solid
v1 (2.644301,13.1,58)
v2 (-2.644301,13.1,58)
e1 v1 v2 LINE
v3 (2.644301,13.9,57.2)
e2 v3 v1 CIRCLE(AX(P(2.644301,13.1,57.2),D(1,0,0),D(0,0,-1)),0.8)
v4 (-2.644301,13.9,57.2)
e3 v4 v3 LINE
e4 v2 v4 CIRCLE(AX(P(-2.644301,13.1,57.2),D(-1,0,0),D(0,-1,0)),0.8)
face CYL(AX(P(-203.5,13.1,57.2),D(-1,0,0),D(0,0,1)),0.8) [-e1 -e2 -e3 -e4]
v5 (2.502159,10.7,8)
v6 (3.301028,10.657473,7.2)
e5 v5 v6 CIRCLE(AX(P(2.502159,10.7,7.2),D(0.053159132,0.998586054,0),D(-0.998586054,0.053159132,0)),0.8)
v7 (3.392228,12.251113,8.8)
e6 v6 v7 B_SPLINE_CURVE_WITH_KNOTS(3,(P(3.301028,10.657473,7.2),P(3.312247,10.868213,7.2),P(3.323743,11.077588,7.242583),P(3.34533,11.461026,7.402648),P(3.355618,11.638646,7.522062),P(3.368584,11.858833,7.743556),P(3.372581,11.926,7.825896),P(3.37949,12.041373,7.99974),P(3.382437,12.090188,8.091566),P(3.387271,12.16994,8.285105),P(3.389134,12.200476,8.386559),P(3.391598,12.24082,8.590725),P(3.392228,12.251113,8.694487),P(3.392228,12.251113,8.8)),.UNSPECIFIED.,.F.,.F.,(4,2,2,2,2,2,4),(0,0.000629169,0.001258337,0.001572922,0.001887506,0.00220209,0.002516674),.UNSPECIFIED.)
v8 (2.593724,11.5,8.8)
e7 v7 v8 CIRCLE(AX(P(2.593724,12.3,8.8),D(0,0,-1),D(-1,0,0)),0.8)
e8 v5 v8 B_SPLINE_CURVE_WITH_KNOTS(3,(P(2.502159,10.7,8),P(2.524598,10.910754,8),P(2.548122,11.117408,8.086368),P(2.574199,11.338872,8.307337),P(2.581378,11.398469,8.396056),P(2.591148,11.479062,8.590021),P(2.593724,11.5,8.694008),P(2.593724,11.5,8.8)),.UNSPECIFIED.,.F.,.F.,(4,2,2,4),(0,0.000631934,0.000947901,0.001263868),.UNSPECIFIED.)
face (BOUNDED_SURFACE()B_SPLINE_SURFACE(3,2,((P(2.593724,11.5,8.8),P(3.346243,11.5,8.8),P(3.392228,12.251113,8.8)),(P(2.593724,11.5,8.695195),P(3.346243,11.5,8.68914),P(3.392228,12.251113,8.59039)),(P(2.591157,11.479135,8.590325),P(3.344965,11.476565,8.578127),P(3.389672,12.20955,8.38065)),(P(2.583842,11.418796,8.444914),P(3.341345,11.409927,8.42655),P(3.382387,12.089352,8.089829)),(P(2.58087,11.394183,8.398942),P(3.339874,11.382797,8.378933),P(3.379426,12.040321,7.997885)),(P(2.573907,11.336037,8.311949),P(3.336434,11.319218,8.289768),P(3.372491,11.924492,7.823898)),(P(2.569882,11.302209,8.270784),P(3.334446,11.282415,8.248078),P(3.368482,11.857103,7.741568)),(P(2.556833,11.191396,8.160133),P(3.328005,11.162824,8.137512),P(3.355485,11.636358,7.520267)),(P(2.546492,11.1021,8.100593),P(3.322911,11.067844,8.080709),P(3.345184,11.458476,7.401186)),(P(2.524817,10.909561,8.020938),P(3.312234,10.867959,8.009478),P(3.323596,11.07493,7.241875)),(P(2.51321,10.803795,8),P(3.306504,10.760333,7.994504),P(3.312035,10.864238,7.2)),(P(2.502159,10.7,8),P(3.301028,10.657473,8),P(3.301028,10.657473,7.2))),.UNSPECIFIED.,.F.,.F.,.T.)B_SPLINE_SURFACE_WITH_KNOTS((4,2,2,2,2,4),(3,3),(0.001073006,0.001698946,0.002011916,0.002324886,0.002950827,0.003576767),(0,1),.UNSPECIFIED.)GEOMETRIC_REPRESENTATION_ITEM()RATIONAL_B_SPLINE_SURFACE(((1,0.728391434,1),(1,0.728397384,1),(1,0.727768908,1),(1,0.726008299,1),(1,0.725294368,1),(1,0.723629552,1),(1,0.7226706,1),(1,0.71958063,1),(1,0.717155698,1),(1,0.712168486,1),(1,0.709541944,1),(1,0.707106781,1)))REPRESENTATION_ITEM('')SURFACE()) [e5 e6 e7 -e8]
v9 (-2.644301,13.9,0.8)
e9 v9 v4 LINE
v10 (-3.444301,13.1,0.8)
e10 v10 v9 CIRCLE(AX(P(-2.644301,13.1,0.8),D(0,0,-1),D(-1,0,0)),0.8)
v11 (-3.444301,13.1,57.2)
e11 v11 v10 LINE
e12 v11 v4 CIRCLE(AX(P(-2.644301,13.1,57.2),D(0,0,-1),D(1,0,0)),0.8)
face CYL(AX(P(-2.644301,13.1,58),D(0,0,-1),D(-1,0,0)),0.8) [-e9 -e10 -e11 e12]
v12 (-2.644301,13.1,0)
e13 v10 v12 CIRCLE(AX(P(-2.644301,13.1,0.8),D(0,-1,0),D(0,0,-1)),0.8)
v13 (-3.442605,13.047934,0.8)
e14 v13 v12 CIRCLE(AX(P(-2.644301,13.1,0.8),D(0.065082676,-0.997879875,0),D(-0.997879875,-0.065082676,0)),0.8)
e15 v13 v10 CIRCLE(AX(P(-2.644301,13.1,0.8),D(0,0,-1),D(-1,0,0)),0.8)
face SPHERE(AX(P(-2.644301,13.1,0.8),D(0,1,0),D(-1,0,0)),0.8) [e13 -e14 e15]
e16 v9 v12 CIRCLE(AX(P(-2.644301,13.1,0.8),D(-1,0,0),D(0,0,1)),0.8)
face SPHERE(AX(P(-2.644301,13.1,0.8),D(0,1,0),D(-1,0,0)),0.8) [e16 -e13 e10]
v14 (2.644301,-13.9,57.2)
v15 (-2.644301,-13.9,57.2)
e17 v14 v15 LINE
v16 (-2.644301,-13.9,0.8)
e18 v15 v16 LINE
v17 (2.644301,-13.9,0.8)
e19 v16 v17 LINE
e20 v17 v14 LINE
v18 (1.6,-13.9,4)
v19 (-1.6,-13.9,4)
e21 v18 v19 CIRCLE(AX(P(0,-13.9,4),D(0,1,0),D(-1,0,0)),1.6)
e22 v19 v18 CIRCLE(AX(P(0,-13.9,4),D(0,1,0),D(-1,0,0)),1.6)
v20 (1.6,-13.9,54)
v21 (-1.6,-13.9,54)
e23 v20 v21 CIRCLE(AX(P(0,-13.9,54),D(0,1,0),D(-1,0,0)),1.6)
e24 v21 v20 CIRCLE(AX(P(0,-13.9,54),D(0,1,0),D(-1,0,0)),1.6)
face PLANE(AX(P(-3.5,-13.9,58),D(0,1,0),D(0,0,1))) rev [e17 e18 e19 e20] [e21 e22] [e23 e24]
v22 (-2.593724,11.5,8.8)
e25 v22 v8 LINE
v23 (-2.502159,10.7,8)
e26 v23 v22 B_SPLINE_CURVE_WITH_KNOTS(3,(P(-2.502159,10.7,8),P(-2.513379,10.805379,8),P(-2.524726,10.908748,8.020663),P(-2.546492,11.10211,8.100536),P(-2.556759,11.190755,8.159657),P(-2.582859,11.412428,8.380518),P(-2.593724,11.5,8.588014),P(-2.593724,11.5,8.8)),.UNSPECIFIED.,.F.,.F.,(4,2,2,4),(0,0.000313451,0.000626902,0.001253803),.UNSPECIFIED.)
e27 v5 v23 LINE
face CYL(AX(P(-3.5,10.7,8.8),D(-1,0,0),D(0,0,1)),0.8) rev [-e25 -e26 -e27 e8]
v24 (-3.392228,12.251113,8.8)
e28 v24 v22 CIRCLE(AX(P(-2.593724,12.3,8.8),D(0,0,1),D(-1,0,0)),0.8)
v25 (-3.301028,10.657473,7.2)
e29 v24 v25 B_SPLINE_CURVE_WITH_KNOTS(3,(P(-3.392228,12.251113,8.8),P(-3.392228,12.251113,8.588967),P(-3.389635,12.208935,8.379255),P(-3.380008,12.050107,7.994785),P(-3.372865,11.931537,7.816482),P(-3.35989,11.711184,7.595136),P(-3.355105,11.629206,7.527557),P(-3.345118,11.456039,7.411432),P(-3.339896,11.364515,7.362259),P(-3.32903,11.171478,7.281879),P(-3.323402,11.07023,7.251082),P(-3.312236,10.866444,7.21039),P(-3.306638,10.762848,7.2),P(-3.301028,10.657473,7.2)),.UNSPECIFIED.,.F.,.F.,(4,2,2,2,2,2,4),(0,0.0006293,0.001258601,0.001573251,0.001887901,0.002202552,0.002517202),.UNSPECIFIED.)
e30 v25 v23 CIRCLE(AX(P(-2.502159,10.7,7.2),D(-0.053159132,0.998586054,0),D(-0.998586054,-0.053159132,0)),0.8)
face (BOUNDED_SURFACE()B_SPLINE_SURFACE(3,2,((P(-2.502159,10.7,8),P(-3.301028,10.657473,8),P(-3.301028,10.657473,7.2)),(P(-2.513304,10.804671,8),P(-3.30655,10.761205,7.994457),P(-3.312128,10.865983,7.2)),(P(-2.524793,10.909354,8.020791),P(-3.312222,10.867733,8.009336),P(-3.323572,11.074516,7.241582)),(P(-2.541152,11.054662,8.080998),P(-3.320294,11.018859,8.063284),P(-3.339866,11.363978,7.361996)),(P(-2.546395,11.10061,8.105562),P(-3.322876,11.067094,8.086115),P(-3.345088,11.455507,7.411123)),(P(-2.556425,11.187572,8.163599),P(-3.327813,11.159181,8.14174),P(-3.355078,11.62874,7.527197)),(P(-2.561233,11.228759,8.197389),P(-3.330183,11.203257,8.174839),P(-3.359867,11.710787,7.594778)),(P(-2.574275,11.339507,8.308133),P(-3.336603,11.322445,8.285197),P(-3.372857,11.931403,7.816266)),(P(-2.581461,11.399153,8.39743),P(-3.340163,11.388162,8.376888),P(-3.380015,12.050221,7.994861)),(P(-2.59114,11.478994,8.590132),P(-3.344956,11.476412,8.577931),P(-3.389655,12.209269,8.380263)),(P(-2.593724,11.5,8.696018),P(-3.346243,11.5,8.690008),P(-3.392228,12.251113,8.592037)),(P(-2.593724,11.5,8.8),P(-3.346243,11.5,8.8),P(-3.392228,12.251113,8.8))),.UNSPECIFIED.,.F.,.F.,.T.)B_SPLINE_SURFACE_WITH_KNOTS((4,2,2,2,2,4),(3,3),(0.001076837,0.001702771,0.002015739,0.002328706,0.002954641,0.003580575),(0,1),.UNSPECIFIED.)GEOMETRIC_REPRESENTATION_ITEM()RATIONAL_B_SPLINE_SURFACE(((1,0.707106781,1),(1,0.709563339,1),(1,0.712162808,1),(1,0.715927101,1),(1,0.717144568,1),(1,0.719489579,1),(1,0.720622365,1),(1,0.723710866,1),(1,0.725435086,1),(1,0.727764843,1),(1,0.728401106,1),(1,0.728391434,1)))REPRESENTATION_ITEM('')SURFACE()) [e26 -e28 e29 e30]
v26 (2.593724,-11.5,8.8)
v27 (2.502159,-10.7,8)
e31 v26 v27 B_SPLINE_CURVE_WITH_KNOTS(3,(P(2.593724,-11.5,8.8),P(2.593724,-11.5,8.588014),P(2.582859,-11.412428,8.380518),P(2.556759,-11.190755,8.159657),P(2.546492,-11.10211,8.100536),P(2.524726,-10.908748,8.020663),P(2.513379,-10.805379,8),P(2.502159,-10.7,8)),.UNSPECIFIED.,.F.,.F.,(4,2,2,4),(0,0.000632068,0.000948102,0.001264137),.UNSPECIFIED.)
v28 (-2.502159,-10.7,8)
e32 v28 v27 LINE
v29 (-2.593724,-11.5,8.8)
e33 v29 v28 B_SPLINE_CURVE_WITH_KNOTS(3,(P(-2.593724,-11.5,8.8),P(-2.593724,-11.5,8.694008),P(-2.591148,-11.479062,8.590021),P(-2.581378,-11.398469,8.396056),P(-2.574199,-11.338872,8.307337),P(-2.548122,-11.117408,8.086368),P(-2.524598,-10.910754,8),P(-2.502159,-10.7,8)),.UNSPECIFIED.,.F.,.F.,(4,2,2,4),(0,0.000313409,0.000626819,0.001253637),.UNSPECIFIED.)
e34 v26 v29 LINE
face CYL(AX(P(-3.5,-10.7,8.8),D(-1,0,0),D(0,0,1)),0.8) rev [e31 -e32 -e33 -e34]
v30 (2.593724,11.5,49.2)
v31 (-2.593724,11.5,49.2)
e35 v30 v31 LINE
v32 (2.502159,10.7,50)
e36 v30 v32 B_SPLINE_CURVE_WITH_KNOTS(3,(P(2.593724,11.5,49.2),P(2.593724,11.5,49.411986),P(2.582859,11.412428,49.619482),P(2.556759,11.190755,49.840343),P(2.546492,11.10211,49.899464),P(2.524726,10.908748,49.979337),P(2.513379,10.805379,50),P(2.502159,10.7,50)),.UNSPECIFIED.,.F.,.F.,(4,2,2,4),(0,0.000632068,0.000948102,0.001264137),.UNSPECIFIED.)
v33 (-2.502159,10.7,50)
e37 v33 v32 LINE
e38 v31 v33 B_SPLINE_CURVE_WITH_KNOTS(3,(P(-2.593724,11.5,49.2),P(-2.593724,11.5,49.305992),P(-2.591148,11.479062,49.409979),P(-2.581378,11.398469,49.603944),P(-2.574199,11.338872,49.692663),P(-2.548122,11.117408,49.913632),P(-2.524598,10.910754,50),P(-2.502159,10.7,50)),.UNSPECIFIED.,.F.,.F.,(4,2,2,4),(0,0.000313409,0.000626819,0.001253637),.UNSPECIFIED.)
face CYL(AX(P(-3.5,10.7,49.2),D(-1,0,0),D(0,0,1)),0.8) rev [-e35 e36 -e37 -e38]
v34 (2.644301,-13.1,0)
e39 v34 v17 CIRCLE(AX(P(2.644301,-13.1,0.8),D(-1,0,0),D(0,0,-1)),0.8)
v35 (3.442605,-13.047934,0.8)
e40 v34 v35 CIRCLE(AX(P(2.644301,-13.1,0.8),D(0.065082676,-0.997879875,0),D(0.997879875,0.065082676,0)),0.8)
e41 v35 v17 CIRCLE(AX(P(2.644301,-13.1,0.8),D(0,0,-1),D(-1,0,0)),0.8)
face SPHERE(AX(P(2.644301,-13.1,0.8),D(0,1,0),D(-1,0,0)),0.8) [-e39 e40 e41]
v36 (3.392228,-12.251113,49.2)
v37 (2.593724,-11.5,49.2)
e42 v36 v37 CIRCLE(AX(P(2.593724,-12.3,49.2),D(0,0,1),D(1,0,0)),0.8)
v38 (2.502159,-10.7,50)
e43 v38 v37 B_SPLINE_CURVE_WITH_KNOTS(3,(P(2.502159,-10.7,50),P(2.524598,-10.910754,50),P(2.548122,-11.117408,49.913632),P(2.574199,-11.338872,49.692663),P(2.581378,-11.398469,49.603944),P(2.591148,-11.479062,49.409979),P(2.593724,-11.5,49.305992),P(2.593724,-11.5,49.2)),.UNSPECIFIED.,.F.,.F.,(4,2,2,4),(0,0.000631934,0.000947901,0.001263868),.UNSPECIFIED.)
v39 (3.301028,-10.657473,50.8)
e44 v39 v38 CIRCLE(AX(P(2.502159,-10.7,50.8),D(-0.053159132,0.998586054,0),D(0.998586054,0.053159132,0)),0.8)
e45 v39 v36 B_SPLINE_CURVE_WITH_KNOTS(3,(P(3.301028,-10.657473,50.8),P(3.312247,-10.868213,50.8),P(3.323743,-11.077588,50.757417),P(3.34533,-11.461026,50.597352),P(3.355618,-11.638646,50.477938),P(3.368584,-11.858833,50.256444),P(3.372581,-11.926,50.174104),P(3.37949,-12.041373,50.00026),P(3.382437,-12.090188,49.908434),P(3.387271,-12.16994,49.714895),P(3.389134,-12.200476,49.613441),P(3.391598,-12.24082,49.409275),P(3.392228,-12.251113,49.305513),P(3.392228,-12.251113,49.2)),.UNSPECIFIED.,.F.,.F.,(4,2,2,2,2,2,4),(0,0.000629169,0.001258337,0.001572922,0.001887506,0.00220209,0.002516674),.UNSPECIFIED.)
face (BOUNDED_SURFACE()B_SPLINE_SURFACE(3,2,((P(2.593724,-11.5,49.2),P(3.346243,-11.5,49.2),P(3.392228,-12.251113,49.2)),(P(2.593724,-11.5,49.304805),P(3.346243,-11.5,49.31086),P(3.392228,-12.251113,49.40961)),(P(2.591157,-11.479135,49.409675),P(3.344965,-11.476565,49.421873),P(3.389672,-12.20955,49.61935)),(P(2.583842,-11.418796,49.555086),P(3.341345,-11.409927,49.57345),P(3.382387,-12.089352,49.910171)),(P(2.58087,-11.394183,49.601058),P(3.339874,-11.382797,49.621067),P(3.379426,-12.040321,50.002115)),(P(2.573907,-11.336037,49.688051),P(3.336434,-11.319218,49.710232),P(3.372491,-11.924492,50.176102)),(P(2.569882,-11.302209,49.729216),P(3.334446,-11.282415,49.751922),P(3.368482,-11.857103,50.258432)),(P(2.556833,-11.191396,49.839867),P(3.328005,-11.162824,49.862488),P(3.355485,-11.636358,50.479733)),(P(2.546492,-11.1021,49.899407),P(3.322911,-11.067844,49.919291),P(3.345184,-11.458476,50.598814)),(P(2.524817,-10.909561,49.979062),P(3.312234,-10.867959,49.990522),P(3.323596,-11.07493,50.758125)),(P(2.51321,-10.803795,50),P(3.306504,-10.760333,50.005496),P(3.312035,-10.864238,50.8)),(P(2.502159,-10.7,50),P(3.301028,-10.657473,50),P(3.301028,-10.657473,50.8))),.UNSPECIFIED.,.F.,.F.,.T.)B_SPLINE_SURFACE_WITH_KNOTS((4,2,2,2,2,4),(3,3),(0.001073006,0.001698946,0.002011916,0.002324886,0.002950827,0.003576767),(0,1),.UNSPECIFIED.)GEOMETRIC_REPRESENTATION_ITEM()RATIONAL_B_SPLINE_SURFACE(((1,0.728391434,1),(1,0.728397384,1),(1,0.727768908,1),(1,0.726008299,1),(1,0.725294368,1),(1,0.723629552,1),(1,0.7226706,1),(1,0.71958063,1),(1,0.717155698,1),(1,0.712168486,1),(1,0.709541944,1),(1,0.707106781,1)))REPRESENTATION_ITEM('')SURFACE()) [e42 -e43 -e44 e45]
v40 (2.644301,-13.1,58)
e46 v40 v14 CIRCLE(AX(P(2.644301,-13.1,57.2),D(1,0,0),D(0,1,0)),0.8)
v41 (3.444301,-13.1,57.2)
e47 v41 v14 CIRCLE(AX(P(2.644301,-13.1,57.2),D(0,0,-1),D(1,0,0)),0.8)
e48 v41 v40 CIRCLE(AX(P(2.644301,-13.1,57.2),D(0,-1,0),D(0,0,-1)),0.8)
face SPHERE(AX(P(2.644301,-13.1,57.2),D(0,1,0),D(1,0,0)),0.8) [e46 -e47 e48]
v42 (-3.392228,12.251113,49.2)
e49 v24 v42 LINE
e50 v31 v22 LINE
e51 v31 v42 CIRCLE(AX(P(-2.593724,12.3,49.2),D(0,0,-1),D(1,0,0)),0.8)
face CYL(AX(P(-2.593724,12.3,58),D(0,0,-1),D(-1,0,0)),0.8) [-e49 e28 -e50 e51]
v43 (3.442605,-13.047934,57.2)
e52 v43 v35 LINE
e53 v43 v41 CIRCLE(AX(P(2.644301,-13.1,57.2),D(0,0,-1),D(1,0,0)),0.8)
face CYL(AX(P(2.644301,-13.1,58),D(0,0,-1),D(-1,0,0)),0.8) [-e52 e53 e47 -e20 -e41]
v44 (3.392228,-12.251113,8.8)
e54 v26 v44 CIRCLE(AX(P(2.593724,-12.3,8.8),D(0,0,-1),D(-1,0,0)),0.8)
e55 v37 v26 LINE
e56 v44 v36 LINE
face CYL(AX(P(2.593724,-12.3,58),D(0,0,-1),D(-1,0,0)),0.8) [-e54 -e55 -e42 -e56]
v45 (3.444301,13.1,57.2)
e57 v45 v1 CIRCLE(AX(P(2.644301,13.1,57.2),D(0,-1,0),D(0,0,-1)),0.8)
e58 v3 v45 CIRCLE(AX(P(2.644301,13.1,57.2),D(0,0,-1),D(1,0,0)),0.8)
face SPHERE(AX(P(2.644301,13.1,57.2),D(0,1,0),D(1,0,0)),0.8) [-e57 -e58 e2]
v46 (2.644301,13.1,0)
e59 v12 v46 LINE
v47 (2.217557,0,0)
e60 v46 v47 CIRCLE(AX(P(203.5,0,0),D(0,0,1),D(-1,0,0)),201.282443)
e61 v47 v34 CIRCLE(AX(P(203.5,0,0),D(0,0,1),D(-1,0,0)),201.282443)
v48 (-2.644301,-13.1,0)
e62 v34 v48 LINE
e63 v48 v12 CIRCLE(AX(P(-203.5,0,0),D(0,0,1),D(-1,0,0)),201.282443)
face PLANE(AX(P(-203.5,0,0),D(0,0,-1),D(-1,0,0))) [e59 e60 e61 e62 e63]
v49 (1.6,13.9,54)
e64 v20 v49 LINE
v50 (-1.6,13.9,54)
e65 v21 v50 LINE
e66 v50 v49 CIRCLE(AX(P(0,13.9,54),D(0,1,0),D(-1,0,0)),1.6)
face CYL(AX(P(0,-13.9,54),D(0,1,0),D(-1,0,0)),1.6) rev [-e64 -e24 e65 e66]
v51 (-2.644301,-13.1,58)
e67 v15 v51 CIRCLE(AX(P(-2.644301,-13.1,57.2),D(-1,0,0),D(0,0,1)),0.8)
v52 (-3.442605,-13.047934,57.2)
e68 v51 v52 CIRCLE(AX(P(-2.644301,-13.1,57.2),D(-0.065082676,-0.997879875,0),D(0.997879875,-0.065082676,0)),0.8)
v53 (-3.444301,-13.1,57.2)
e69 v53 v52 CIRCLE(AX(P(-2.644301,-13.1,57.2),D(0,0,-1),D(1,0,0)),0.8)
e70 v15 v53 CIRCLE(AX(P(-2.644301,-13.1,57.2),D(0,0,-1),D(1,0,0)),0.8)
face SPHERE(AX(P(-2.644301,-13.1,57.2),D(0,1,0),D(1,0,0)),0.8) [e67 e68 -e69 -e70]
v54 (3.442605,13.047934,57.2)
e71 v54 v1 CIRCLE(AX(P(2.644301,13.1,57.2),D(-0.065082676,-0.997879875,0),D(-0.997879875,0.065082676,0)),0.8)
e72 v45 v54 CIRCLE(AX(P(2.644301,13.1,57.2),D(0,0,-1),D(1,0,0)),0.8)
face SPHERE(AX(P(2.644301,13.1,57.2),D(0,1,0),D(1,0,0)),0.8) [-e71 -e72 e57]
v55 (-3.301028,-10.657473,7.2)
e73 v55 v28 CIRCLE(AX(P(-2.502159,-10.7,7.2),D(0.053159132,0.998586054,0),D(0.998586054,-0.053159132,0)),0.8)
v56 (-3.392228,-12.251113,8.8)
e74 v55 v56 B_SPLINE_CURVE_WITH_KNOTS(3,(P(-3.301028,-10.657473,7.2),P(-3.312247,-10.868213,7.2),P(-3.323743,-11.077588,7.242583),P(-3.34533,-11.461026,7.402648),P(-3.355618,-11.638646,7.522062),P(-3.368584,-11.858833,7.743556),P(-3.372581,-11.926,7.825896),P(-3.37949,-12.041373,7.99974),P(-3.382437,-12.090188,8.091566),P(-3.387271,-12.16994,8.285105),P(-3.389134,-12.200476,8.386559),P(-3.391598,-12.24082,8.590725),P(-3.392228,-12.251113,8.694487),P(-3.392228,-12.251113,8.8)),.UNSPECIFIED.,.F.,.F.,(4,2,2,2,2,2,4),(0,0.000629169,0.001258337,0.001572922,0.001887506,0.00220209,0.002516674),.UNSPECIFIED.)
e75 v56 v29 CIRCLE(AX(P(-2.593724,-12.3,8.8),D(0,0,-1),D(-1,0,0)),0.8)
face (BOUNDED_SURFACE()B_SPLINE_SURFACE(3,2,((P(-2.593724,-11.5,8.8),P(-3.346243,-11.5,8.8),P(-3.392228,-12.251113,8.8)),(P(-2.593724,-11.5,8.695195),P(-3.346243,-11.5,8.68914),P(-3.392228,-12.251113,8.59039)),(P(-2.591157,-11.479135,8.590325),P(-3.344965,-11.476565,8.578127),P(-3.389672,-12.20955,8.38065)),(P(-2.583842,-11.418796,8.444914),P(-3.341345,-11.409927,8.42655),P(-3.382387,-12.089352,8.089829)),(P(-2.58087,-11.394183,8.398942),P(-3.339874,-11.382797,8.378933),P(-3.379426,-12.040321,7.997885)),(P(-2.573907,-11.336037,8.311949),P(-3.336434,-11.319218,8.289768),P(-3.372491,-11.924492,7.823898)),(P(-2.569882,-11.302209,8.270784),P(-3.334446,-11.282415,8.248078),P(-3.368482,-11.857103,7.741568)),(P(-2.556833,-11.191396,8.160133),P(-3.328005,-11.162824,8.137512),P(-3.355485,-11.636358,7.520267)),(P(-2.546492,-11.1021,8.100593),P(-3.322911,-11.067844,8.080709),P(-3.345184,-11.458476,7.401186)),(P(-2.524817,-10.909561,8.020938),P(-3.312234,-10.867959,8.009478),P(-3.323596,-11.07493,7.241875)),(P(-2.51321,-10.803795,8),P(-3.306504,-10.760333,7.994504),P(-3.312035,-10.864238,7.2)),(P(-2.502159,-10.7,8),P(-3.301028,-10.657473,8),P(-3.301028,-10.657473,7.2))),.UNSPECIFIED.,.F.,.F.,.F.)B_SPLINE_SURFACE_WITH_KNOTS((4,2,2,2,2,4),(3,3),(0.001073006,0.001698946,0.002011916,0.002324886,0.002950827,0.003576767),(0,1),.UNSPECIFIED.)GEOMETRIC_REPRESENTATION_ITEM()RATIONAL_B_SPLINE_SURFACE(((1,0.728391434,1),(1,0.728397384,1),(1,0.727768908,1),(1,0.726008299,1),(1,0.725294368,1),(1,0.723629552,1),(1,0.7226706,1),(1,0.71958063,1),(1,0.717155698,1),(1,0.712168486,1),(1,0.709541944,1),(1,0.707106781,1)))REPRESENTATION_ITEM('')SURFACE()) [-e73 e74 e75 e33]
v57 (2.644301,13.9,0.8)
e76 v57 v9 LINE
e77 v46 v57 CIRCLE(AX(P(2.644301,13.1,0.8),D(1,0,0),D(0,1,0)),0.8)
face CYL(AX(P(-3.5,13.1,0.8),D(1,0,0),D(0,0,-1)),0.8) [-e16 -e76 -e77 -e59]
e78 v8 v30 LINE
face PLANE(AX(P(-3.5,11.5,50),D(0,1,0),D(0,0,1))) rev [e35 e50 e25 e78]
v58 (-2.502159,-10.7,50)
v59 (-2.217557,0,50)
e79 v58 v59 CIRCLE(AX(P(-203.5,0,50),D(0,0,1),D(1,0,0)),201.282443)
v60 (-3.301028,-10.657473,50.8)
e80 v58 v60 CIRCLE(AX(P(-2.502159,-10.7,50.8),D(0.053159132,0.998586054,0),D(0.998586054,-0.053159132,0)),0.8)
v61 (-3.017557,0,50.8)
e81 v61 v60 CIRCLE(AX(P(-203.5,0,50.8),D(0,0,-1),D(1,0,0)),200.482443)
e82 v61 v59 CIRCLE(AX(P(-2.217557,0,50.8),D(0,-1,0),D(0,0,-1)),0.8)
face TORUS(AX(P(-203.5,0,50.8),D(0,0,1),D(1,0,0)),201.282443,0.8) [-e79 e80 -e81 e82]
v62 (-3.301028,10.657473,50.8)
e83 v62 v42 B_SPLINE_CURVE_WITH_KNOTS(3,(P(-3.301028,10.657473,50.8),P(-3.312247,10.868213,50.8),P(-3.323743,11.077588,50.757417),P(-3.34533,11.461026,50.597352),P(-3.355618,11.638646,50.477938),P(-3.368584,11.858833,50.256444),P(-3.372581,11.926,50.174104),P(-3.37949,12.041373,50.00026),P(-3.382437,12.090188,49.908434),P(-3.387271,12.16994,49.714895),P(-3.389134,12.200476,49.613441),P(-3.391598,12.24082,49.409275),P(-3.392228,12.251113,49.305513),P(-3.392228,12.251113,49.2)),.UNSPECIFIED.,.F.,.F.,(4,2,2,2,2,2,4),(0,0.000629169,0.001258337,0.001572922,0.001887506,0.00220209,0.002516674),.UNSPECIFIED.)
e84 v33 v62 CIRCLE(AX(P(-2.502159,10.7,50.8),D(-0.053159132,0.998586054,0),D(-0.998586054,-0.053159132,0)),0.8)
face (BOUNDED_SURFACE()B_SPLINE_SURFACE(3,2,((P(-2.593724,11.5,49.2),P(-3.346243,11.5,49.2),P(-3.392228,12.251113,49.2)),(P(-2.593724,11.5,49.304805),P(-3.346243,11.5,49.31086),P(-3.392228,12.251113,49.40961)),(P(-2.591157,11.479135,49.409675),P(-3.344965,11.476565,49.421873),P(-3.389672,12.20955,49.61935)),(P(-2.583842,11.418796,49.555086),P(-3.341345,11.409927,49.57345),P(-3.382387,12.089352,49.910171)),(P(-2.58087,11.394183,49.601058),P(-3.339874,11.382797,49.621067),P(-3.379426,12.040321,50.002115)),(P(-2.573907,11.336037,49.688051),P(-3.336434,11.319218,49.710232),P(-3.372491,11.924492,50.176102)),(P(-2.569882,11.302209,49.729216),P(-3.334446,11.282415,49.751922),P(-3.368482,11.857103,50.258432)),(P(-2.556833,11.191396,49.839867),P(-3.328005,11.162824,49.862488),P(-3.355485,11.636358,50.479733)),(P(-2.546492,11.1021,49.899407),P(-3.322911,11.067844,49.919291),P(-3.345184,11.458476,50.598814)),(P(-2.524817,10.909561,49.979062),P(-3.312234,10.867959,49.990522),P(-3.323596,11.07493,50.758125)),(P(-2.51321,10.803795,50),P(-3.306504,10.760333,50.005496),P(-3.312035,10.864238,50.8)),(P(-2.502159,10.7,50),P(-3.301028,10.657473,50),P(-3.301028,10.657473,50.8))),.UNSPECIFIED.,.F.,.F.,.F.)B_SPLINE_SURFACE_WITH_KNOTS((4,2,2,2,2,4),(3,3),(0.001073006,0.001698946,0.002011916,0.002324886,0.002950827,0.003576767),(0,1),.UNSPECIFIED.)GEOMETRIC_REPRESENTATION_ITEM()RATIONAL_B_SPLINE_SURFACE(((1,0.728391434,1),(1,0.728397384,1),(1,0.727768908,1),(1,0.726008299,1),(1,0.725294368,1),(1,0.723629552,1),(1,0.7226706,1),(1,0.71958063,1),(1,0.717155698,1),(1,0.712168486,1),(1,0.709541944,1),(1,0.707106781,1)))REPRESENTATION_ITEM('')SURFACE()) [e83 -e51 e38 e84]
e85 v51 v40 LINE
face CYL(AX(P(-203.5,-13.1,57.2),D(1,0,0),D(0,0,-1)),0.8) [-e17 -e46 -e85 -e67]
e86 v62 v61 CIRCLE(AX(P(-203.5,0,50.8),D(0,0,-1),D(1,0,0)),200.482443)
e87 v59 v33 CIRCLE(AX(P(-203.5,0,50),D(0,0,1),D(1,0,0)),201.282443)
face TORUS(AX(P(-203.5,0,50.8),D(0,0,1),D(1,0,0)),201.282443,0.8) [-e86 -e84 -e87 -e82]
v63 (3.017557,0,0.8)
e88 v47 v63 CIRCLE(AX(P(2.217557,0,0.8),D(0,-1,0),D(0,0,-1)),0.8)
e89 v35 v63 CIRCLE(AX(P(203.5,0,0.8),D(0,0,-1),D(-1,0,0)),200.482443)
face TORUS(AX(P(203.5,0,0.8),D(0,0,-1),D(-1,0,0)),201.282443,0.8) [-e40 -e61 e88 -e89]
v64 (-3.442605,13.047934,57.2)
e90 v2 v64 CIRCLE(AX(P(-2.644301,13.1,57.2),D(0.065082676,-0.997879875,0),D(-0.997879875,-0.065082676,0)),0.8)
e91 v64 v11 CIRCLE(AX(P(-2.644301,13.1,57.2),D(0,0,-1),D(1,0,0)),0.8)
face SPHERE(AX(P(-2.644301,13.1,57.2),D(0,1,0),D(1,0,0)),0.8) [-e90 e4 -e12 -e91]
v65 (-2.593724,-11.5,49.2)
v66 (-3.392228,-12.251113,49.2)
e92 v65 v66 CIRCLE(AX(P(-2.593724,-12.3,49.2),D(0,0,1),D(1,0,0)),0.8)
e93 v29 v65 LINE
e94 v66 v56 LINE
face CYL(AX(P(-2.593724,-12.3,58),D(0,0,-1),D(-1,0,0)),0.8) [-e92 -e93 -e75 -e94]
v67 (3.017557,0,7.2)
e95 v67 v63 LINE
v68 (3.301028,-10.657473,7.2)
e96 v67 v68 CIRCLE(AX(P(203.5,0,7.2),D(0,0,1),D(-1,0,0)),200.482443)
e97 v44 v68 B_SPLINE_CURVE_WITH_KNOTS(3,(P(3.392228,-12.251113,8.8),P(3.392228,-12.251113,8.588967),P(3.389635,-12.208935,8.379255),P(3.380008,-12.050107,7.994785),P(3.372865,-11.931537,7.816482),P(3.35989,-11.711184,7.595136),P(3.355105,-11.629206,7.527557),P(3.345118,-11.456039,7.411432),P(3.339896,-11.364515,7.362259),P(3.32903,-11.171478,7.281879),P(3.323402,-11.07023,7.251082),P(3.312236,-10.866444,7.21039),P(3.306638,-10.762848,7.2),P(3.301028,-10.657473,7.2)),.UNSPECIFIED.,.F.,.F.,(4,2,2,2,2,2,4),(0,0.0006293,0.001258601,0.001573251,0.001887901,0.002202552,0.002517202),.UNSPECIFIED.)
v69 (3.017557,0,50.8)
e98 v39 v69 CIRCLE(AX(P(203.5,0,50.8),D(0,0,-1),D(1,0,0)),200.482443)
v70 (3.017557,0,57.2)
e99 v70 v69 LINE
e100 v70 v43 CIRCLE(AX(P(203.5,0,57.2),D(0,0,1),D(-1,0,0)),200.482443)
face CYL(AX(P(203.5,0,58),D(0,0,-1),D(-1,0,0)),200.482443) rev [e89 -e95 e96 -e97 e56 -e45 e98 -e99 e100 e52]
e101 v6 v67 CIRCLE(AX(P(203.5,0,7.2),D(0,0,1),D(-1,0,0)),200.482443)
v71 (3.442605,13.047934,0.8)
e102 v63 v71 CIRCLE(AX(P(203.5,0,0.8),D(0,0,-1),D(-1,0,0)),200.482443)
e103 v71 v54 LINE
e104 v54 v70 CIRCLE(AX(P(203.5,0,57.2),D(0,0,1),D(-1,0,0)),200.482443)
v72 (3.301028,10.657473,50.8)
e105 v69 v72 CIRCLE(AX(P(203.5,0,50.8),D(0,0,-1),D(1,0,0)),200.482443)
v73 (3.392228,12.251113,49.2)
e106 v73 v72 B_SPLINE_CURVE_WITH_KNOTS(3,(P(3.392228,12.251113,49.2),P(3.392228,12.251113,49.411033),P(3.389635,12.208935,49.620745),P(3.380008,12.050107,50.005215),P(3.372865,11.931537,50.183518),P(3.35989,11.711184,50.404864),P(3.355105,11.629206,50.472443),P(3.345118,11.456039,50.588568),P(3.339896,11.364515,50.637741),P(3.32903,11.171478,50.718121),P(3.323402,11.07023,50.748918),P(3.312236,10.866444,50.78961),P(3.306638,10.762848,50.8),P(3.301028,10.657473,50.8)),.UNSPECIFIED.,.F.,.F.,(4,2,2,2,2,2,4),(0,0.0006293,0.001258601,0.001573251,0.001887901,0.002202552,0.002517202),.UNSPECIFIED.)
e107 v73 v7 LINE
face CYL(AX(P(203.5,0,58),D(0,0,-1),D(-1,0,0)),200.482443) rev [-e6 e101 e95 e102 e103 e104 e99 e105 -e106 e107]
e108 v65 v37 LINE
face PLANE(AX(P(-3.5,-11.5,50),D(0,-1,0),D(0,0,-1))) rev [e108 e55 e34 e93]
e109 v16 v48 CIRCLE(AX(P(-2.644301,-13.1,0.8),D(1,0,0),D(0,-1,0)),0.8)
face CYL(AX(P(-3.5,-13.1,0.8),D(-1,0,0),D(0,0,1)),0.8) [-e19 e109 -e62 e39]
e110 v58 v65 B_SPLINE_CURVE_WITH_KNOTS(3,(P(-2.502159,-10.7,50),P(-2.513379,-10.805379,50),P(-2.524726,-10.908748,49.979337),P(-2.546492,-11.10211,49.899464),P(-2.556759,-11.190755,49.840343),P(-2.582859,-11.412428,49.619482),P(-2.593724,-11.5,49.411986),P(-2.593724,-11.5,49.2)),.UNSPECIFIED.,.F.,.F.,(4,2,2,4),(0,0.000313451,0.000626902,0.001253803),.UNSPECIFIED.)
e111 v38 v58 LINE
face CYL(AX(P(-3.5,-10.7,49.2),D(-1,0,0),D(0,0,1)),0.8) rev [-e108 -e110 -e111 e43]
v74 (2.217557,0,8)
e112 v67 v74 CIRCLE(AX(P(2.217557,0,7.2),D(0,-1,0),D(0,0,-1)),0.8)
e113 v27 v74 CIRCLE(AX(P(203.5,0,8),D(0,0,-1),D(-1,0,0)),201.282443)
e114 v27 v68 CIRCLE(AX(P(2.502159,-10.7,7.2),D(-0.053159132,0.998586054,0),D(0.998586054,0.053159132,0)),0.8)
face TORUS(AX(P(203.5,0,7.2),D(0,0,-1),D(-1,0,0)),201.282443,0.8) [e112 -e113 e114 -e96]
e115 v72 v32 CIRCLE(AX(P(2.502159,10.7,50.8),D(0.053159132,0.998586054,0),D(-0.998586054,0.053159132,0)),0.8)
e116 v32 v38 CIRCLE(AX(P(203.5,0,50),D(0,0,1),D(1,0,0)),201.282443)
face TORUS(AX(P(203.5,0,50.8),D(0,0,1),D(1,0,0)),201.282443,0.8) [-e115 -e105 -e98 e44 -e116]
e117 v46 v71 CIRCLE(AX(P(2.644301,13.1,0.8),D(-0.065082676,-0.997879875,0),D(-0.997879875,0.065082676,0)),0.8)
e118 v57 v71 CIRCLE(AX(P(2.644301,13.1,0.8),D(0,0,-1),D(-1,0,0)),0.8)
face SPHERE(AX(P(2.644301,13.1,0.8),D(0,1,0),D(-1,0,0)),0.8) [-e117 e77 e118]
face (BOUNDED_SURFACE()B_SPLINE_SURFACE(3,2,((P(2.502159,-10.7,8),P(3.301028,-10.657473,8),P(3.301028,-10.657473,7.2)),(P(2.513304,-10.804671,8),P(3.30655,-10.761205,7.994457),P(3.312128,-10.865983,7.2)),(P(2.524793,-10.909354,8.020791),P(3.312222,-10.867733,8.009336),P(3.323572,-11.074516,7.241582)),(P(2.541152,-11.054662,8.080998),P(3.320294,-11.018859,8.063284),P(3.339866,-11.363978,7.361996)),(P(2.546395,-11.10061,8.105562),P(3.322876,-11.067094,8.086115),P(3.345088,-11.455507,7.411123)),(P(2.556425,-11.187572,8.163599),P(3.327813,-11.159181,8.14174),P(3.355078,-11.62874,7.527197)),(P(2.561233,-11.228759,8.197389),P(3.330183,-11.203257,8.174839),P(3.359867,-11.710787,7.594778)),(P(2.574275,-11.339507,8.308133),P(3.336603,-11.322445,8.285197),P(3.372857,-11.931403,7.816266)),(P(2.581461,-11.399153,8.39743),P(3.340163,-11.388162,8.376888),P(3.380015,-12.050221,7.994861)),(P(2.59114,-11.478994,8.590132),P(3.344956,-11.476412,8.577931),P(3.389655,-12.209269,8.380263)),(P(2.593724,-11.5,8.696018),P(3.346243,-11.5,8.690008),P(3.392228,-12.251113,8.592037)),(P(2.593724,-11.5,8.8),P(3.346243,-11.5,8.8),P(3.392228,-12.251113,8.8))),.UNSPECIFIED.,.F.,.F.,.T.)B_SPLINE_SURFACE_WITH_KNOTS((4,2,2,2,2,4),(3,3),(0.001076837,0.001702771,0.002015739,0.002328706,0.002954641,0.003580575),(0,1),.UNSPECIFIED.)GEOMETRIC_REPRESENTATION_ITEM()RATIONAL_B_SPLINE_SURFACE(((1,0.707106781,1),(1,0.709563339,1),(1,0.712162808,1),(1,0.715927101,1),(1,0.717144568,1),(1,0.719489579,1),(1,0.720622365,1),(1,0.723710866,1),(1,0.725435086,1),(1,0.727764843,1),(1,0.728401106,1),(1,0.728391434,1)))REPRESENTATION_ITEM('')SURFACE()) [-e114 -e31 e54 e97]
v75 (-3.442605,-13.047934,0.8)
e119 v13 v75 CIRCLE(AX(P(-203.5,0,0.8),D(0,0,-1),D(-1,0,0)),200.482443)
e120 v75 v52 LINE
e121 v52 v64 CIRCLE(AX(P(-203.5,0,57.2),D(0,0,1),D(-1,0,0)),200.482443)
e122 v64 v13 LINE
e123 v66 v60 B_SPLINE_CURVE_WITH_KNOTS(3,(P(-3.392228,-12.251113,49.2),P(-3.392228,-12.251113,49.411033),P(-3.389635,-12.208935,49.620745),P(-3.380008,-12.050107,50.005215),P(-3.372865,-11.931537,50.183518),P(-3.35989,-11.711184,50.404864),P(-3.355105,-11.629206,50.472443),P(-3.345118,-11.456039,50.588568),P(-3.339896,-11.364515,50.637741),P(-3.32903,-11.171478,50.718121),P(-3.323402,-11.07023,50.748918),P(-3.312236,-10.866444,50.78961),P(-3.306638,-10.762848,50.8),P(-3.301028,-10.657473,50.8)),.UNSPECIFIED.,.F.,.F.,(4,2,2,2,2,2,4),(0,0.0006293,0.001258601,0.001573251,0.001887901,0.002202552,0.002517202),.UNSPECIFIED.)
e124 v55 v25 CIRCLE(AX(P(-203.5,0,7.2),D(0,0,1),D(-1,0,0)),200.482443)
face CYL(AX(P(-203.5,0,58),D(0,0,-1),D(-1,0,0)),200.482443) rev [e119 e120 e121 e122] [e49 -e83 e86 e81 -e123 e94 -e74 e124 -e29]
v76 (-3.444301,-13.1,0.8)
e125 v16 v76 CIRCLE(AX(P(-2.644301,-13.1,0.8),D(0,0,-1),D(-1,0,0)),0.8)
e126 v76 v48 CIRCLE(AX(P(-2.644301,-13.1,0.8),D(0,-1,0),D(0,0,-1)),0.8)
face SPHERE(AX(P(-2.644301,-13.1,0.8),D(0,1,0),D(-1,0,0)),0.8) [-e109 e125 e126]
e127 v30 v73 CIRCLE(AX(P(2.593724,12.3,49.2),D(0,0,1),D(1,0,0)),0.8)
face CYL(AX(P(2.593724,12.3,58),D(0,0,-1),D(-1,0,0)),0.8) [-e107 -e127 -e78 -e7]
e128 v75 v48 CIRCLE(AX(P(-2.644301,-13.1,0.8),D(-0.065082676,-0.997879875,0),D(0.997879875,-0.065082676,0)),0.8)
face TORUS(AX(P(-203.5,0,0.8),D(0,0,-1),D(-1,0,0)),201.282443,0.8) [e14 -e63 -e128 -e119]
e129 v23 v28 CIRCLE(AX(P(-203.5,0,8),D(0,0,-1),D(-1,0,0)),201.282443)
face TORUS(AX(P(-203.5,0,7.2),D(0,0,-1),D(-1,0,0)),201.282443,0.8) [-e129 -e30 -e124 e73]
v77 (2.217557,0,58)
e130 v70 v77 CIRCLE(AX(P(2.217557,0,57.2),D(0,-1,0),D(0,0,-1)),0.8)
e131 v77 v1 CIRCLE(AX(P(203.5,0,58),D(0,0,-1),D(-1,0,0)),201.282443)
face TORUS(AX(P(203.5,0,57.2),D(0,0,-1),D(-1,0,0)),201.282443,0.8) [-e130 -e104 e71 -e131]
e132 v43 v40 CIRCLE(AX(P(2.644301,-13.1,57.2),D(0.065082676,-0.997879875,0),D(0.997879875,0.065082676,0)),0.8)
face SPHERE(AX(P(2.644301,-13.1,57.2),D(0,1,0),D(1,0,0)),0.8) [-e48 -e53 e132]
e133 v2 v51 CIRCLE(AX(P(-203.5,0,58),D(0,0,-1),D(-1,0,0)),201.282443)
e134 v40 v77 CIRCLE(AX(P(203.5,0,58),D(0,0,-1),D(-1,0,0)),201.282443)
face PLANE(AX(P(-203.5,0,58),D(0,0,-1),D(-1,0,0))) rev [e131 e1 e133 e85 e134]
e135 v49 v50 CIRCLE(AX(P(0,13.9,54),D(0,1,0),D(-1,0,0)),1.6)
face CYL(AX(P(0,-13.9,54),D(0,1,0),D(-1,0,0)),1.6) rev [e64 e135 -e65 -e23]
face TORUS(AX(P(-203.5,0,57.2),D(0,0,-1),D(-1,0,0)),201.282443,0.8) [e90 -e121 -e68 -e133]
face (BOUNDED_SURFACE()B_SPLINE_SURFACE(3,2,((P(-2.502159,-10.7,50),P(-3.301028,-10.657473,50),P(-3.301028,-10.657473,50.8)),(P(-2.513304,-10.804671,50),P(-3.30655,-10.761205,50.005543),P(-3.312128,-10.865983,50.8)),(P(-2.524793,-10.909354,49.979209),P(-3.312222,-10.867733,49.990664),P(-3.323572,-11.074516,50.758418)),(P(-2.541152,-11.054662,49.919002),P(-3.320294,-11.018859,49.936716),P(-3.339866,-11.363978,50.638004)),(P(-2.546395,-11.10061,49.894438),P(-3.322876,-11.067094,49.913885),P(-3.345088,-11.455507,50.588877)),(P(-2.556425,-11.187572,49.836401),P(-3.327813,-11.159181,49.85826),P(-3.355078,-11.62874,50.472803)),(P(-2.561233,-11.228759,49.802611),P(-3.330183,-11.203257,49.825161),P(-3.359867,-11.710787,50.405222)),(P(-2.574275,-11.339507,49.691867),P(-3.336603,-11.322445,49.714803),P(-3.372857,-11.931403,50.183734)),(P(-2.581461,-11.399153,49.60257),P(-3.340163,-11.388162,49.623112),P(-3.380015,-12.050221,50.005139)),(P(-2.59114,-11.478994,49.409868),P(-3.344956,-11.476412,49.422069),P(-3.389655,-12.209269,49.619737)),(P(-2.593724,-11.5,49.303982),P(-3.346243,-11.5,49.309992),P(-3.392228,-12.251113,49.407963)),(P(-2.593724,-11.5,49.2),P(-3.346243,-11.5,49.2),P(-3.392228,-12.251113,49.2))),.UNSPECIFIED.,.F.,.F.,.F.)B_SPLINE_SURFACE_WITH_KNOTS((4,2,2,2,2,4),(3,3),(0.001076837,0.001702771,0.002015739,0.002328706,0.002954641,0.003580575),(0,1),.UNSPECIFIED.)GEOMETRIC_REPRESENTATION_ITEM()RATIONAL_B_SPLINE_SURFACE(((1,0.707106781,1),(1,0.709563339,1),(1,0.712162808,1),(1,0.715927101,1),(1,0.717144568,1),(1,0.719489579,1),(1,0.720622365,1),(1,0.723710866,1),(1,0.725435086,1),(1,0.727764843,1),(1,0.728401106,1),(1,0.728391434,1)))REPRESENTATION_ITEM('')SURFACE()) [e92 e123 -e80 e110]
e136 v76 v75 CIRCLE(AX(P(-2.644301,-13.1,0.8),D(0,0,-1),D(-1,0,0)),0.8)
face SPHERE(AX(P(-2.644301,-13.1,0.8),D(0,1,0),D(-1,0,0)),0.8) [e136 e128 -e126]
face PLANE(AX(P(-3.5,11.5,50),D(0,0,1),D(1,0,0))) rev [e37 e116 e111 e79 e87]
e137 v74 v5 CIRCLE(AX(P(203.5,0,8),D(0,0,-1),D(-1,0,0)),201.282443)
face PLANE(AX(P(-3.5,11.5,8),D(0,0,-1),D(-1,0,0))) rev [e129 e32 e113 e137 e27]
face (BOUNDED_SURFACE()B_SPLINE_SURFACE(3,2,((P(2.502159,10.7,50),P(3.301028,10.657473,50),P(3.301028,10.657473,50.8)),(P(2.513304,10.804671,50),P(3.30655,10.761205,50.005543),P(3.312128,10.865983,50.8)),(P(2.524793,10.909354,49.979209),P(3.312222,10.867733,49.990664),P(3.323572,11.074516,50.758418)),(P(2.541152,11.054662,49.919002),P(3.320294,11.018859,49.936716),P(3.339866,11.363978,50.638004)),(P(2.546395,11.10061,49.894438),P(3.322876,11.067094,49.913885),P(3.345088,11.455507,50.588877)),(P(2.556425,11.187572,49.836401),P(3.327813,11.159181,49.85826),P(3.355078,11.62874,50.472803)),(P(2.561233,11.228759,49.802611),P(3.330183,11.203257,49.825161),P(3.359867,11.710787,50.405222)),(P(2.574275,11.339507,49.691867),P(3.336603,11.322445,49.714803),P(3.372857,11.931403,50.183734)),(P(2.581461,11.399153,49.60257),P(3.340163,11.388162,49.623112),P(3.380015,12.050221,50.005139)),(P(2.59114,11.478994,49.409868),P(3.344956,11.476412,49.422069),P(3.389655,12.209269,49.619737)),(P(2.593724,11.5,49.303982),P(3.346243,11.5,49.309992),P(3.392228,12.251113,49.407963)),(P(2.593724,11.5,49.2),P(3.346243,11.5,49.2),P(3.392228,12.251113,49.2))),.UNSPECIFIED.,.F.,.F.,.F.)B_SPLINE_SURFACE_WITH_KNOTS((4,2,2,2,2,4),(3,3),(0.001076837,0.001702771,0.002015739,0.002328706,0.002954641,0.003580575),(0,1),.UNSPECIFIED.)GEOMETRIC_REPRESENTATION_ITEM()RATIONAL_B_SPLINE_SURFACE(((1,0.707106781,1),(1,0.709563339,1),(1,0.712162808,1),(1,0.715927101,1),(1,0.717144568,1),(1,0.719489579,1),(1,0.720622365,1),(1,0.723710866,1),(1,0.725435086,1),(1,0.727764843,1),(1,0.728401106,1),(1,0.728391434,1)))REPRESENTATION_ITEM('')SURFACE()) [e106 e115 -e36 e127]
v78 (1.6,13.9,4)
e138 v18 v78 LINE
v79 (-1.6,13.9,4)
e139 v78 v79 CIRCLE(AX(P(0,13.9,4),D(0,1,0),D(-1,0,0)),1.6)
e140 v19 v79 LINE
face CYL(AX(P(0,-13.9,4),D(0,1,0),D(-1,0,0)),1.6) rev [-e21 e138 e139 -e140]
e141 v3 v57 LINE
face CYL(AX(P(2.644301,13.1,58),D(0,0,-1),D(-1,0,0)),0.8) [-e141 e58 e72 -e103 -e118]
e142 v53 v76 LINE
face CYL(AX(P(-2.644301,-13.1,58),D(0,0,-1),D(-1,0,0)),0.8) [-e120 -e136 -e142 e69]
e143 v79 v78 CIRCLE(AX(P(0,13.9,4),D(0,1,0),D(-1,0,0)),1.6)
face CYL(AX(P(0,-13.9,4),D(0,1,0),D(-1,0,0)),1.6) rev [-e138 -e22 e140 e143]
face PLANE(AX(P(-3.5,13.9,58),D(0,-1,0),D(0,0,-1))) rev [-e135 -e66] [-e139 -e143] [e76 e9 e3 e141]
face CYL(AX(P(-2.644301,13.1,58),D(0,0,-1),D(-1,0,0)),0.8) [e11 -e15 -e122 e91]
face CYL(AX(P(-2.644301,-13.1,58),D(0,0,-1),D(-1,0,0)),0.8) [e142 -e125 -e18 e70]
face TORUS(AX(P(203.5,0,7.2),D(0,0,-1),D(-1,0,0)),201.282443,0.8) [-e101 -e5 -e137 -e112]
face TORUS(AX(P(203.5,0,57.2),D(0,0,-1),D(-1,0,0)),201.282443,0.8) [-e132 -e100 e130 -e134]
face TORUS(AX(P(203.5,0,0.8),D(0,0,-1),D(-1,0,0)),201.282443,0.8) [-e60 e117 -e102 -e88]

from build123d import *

# Parameters (mm, degrees)
EXTRUDE_1_DEPTH          = 58
CUT_EXTRUDE_1_DEPTH      = 60.744957946
CUT_EXTRUDE_1_DEPTH_BACK = 60.744957946
SKETCH_2_W               = 42
SKETCH_2_H               = 23
SKETCH_3_R               = 1.6
CUT_EXTRUDE_2_DEPTH      = 65.413430277
FILLET_1_R               = 0.8


with BuildPart() as part:
    # 草图1 → 凸台-拉伸1 (new body)
    with BuildSketch(Plane.XY):
        with BuildLine():
            Line((-3.5, 13.9), (3.5, 13.9))
            ThreePointArc((3.5, 13.9), (3.017556878, 0), (3.5, -13.9))
            Line((3.5, -13.9), (-3.5, -13.9))
            ThreePointArc((-3.5, -13.9), (-3.017556878, 0), (-3.5, 13.9))
        make_face()
    extrude(amount=EXTRUDE_1_DEPTH)

    # 草图2 → 切除-拉伸1 (cut, two sides: drawn at the far end of the back side and taken through both)
    with BuildSketch(Plane(origin=(0, 0, 0), x_dir=(0, 0, -1), z_dir=(1, 0, 0)).offset(-CUT_EXTRUDE_1_DEPTH_BACK)):
        with Locations((-29, 0)):
            Rectangle(SKETCH_2_W, SKETCH_2_H)
    extrude(amount=CUT_EXTRUDE_1_DEPTH + CUT_EXTRUDE_1_DEPTH_BACK, mode=Mode.SUBTRACT)

    # 草图3 → 切除-拉伸2 (cut, through all)
    with BuildSketch(Plane(origin=(0, 13.9, 0), x_dir=(1, 0, 0), z_dir=(0, 1, 0))):
        with Locations(Location((0, -4, 0), (0, 0, 180))):
            Circle(SKETCH_3_R)
        with Locations(Location((0, -54, 0), (0, 0, 180))):
            Circle(SKETCH_3_R)
    extrude(amount=-CUT_EXTRUDE_2_DEPTH, mode=Mode.SUBTRACT)

    # 圆角1
    fillet_1_edges = [part.edges().sort_by_distance(p)[0] for p in [
        (3.017556878, 0, 58),
        (3.34765802, 11.5, 29),
        (3.017556878, 0, 50),
        (3.34765802, -11.5, 29),
        (3.017556878, 0, 8),
        (0, 13.9, 58),
        (-3.017556878, 0, 8),
        (0, 11.5, 8),
        (-3.34765802, -11.5, 29),
        (0, -11.5, 8),
        (-3.017556878, 0, 50),
        (0, -11.5, 50),
        (-3.34765802, 11.5, 29),
        (0, 11.5, 50),
        (-3.017556878, 0, 58),
        (0, 13.9, 0),
        (3.017556878, 0, 0),
        (0, -13.9, 0),
        (-3.017556878, 0, 0),
        (-3.5, 13.9, 29),
        (3.5, 13.9, 29),
        (3.5, -13.9, 29),
        (-3.5, -13.9, 29),
        (0, -13.9, 58),
    ]]
    fillet(fillet_1_edges, radius=FILLET_1_R)


solid = part.part
